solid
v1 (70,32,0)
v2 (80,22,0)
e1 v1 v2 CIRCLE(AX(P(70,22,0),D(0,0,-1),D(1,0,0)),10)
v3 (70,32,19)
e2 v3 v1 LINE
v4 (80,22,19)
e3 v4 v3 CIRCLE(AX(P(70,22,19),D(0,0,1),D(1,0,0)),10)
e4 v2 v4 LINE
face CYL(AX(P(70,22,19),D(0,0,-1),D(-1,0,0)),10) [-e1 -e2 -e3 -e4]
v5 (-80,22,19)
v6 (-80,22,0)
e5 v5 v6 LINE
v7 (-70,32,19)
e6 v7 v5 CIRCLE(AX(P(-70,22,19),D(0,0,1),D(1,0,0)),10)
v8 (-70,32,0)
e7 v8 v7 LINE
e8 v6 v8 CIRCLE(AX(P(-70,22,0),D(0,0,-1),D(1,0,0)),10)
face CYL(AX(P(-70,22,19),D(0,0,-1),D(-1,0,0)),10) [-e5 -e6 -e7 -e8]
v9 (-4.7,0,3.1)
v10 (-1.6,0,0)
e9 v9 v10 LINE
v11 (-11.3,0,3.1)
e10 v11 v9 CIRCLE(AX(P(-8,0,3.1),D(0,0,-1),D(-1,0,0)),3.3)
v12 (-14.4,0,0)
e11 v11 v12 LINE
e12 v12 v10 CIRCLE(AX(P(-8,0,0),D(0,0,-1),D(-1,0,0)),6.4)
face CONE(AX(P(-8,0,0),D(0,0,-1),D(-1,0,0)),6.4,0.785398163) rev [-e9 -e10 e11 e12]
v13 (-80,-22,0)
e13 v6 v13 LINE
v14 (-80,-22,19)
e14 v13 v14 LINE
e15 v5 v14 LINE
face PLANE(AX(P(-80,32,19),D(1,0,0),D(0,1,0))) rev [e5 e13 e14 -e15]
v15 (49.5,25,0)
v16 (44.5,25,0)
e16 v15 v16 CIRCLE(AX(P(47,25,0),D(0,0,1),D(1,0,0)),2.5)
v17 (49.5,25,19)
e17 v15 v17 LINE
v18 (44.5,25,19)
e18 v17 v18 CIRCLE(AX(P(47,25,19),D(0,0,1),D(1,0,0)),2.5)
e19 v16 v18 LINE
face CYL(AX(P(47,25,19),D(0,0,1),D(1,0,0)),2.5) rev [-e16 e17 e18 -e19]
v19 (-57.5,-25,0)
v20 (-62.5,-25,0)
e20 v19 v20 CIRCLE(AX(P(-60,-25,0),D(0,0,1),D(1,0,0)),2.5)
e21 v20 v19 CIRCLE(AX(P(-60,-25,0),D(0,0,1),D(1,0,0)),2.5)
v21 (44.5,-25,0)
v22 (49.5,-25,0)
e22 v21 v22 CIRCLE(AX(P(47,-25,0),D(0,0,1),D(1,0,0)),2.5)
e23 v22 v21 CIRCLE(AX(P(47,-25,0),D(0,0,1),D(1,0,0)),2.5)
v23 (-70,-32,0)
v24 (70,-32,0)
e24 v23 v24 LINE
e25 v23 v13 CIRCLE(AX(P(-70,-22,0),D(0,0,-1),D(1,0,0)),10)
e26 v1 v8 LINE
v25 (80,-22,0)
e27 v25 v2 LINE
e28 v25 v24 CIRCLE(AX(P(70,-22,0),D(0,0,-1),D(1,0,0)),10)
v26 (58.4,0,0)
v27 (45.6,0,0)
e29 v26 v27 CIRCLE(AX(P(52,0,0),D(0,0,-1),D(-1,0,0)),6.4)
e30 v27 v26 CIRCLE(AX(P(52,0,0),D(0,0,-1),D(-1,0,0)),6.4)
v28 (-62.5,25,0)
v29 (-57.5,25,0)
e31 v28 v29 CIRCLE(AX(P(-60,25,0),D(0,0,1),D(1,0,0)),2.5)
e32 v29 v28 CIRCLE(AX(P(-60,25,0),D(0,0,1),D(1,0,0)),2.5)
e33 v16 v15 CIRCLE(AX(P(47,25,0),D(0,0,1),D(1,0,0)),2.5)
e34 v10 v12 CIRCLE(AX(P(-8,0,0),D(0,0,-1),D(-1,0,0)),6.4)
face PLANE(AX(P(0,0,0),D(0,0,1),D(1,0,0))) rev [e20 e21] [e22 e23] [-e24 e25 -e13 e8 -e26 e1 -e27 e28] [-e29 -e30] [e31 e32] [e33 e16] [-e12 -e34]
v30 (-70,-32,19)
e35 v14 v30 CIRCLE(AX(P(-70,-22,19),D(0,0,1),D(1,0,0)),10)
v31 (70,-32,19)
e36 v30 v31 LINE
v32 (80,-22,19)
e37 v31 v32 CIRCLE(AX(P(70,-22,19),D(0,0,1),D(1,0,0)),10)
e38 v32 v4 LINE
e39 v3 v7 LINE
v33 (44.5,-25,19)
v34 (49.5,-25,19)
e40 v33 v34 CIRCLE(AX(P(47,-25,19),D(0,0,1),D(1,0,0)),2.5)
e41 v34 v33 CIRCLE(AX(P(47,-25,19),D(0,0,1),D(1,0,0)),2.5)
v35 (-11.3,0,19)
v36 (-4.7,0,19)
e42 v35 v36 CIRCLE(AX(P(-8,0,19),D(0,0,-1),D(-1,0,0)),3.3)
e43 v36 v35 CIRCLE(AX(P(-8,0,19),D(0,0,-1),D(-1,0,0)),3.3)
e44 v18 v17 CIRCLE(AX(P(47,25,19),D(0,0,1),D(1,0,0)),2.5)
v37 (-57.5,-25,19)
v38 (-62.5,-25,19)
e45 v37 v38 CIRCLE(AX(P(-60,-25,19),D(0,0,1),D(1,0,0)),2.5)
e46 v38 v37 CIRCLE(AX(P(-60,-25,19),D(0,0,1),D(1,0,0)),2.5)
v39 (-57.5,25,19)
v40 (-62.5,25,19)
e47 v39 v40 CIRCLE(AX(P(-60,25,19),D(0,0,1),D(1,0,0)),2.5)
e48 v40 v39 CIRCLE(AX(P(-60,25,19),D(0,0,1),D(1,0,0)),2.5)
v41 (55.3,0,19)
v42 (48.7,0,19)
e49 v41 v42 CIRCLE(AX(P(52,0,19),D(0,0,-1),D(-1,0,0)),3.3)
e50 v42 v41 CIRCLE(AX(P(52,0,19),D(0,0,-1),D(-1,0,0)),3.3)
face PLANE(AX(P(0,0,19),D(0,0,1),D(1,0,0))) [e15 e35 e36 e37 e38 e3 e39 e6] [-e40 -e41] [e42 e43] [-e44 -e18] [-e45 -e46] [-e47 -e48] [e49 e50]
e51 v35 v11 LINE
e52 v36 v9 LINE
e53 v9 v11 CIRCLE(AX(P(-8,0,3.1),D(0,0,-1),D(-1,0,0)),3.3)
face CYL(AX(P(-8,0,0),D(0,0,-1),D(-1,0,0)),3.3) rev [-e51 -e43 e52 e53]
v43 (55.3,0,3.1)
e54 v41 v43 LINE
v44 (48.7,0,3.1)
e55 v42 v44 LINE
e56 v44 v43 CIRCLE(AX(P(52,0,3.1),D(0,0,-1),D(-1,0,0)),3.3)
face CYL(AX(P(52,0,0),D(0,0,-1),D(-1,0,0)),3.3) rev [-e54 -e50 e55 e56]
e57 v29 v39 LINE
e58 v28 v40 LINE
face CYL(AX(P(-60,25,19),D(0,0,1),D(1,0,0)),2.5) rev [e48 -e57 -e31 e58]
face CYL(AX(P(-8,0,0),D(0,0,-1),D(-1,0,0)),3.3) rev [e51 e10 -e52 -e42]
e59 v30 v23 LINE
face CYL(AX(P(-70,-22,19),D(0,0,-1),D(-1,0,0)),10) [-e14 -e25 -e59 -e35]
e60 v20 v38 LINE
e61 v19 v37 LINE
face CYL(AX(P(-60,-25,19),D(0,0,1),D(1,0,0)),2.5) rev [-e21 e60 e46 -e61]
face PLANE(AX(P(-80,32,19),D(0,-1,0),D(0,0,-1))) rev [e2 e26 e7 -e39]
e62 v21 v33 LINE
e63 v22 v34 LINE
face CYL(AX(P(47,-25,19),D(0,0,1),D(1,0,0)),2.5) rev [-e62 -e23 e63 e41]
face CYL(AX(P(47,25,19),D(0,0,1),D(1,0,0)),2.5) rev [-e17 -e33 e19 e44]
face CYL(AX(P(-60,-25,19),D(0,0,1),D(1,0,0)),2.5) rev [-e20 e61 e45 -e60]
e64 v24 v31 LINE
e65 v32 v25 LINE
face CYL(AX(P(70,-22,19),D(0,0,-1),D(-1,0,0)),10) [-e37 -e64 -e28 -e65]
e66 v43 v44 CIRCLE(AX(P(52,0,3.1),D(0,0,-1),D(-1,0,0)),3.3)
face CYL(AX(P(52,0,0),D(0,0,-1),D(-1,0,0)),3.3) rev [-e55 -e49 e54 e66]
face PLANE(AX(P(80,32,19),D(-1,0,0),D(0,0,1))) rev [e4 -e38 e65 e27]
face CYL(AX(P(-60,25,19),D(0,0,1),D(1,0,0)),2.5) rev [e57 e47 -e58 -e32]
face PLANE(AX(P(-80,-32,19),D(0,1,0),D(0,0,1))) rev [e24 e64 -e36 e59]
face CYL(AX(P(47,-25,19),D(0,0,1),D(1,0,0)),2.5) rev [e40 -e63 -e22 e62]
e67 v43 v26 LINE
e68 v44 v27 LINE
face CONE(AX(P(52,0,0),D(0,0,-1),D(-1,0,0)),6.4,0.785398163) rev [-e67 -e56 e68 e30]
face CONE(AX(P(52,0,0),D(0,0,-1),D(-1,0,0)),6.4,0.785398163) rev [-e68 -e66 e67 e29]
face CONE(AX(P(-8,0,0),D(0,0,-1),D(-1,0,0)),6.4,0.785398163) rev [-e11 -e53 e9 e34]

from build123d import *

# Parameters (mm, degrees)
SKETCH_1_W                = 160
SKETCH_1_H                = 64
EXTRUDE_1_DEPTH           = 19
FILLET_1_R                = 10
HOLE_WIZARD_M6_1_D        = 5
HOLE_WIZARD_2_D           = 6.6
HOLE_WIZARD_2_CSINK_D     = 12.8
HOLE_WIZARD_2_CSINK_ANGLE = 90


with BuildPart() as part:
    # 草图1 → 凸台-拉伸1 (new body)
    with BuildSketch(Plane.XY):
        Rectangle(SKETCH_1_W, SKETCH_1_H)
    extrude(amount=EXTRUDE_1_DEPTH)

    # 圆角1
    fillet_1_edges = [part.edges().sort_by_distance(p)[0] for p in [
        (80, -32, 9.5),
        (-80, -32, 9.5),
        (-80, 32, 9.5),
        (80, 32, 9.5),
    ]]
    fillet(fillet_1_edges, radius=FILLET_1_R)

    # M6 螺纹孔1 (through all)
    with Locations(Plane.XY.offset(19)):
        with Locations((-60, 25), (-60, -25), (47, 25), (47, -25)):
            Hole(HOLE_WIZARD_M6_1_D / 2)

    # 打孔尺寸(%根据)内六角花形半沉头螺钉的类型2 (through all)
    with Locations(Plane(origin=(0, 0, 0), x_dir=(-1, 0, 0), z_dir=(0, 0, -1))):
        with Locations((-52, 0), (8, 0)):
            CounterSinkHole(HOLE_WIZARD_2_D / 2, HOLE_WIZARD_2_CSINK_D / 2, counter_sink_angle=HOLE_WIZARD_2_CSINK_ANGLE)


solid = part.part
